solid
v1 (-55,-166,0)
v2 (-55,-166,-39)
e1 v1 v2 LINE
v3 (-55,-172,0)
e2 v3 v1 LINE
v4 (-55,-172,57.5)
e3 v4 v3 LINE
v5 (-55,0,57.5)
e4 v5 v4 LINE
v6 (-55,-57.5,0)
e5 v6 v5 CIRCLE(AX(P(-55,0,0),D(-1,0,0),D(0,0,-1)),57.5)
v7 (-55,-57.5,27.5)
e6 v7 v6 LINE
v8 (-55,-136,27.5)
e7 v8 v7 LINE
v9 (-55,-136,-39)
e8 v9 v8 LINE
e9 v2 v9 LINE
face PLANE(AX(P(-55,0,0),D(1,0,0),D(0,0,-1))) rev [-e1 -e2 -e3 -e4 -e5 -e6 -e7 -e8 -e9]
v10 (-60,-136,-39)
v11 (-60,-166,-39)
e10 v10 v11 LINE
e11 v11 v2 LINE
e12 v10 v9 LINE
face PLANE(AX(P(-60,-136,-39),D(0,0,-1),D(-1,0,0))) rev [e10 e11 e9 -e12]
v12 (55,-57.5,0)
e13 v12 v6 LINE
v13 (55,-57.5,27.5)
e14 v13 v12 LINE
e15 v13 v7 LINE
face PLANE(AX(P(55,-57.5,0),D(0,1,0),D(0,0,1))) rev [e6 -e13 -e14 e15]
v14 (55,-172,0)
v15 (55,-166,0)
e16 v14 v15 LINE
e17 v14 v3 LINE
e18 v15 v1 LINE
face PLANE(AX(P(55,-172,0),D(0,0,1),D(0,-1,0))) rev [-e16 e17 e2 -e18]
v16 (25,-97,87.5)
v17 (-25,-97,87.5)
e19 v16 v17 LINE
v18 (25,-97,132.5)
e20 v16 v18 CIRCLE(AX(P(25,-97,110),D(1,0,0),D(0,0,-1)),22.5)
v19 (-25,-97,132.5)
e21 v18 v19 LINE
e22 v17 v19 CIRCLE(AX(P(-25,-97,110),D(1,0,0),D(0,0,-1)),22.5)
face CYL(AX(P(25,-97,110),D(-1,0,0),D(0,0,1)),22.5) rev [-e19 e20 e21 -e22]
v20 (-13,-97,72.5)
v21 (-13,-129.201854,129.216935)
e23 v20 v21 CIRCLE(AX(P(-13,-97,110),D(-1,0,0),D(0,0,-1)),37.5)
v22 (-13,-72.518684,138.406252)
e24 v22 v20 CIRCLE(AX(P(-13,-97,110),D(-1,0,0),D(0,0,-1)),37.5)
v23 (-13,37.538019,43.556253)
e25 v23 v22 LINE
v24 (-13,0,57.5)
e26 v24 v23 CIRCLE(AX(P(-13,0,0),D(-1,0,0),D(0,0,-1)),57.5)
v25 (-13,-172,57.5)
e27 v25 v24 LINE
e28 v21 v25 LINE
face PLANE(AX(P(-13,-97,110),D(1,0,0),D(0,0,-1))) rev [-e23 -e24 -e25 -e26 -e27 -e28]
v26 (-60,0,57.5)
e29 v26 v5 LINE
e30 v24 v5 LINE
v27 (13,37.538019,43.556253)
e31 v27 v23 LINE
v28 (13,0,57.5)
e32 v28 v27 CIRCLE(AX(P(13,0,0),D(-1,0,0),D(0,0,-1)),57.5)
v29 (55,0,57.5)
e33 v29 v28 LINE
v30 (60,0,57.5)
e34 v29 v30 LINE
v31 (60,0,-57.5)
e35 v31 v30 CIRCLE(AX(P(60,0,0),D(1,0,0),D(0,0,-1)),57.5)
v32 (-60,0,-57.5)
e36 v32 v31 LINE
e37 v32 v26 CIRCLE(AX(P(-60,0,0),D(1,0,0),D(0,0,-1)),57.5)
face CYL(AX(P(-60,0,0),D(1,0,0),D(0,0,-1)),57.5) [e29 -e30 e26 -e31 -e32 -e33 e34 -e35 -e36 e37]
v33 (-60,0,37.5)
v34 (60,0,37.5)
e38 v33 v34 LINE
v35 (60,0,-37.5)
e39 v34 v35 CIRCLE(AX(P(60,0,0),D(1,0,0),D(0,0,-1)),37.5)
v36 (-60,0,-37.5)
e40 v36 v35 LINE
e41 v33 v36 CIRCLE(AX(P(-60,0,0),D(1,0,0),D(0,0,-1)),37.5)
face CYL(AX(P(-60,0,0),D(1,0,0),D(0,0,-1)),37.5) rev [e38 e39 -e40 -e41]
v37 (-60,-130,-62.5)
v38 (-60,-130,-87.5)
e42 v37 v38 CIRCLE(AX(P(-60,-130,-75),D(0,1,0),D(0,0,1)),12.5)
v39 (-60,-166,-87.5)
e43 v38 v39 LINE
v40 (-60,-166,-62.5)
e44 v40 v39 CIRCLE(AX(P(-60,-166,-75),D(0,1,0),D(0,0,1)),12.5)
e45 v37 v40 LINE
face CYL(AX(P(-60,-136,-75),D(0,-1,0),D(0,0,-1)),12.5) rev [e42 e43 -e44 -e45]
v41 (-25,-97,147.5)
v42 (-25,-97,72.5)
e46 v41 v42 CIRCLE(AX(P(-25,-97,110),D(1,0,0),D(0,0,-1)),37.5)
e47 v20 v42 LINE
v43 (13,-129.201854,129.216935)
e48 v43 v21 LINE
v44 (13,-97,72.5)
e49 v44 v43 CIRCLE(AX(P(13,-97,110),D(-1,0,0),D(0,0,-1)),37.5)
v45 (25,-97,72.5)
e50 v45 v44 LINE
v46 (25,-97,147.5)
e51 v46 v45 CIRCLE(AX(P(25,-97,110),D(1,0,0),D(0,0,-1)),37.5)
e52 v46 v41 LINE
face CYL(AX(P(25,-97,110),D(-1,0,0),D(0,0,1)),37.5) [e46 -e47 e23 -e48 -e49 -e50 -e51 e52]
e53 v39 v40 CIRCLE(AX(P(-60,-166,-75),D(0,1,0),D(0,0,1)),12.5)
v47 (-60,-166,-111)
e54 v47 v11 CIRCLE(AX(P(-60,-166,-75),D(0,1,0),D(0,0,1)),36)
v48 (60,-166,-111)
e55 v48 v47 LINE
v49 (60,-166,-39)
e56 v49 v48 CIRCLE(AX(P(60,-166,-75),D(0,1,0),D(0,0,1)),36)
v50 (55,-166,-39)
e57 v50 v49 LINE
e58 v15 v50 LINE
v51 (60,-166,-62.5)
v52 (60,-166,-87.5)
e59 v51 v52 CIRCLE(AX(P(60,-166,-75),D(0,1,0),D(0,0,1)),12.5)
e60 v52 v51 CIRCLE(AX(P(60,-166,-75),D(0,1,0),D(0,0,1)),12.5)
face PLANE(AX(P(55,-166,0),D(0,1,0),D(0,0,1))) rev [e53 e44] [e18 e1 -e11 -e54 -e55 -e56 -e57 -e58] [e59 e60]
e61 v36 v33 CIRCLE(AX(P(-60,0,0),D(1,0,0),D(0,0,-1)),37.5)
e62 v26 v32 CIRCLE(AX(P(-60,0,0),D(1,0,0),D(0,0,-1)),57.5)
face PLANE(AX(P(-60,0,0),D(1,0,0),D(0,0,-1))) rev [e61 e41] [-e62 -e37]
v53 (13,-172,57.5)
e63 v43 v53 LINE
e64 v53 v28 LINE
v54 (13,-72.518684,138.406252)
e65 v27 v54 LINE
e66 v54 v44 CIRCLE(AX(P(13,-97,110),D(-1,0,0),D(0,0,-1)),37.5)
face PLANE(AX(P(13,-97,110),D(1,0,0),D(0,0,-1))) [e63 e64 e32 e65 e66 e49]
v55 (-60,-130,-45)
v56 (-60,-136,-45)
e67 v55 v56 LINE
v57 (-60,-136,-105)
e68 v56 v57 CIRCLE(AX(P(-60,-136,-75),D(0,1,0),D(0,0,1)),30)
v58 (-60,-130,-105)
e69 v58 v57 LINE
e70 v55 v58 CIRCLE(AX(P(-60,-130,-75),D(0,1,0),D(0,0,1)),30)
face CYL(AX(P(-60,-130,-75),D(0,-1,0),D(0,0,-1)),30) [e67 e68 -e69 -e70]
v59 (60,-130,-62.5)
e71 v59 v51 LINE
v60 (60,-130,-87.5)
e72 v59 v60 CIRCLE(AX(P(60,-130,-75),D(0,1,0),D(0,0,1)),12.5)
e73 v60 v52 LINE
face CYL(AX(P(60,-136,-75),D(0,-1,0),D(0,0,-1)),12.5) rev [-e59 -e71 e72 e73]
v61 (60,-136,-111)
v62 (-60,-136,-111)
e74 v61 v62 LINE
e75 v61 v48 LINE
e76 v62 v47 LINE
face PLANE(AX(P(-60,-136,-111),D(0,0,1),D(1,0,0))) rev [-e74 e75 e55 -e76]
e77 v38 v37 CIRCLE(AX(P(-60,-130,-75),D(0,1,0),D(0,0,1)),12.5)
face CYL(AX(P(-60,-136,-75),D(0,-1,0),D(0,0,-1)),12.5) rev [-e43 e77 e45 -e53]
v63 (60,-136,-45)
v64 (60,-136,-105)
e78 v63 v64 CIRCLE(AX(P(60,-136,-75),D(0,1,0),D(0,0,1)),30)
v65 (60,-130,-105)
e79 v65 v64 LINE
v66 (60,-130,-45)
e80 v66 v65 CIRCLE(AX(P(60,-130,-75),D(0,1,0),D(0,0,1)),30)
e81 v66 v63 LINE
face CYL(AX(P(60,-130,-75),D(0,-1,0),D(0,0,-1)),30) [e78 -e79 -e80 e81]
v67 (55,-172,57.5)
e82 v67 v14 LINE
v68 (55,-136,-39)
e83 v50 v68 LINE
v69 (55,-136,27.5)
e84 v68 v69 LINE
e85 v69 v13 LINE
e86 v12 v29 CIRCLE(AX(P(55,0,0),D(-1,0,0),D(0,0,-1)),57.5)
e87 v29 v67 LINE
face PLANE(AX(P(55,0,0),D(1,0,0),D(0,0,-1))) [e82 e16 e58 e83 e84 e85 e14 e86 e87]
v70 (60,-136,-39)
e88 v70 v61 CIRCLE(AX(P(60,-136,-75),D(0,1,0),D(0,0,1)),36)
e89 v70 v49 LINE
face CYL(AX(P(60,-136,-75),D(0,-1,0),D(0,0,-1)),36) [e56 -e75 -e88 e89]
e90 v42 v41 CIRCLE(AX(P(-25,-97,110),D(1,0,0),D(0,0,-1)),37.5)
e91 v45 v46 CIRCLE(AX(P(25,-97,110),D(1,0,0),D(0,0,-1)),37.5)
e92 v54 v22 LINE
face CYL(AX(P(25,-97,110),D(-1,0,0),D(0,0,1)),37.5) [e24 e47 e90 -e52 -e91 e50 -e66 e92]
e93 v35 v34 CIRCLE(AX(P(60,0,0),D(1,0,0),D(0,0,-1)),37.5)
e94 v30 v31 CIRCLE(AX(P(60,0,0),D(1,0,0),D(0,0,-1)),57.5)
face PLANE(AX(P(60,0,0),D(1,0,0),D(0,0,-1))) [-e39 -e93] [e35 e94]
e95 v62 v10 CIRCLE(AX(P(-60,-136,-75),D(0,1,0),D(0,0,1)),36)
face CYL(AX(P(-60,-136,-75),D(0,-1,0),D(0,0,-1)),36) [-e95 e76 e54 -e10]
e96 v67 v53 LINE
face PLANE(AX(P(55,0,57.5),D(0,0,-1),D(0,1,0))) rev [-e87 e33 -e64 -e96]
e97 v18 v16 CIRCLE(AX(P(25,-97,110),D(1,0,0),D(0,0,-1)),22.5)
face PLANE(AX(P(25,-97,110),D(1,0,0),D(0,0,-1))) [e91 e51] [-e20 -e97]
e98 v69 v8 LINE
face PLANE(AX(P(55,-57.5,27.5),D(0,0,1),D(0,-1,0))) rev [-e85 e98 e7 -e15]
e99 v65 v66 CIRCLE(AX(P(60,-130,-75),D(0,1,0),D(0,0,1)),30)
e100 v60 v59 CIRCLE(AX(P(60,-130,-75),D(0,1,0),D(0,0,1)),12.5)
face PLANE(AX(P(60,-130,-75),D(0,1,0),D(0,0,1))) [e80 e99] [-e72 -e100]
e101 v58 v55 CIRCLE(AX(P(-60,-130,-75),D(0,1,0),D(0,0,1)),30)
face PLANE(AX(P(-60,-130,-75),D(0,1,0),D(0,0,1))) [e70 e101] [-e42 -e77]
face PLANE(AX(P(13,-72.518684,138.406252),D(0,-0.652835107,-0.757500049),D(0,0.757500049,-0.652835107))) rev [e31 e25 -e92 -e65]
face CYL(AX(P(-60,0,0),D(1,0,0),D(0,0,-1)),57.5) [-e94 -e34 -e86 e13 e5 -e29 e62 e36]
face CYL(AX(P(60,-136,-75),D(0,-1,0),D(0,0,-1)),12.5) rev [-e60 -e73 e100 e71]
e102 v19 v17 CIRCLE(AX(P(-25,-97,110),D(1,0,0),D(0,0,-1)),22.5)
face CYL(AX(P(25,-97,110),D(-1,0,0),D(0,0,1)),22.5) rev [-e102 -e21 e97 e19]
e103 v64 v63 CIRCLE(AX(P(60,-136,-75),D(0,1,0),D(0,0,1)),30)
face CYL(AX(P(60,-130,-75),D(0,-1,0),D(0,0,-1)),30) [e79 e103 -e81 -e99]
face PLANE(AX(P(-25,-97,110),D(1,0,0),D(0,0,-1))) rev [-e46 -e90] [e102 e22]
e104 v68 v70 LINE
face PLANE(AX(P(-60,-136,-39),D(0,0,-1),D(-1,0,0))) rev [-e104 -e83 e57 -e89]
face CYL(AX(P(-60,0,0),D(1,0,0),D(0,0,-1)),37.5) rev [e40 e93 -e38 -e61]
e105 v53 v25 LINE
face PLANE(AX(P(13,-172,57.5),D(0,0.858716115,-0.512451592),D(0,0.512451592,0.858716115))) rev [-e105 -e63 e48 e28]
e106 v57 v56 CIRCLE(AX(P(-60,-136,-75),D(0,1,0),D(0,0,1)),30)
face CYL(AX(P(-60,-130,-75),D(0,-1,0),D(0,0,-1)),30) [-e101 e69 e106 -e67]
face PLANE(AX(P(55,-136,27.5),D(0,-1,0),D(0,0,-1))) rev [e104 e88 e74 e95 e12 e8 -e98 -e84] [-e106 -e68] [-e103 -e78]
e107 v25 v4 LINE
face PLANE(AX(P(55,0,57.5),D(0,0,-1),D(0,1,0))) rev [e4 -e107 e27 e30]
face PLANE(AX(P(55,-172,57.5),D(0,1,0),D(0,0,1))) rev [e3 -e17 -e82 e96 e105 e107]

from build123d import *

# Parameters (mm, degrees)
BEARING_HOUSING_SKETCH_R   = 57.5
BEARING_HOUSING_SKETCH_R_2 = 37.5
BEARING_HOUSING_115_DEPTH  = 60
BASE_FOOT_SKETCH_R         = 12.5
BASE_FOOT_DEPTH            = 30
MOUNTING_PAD_SKETCH_R      = 30
MOUNTING_PAD_SKETCH_R_2    = 12.5
MOUNTING_PAD_DEPTH         = 6
SUPPORT_WEB_DEPTH          = 55
SIDE_BOSS_SKETCH_R         = 37.5
SIDE_BOSS_SKETCH_R_2       = 22.5
SIDE_BOSS_75_DEPTH         = 25
GUSSET_RIB_DEPTH           = 13


with BuildPart() as part:
    # Bearing Housing Sketch → Bearing Housing Ø115 (new, symmetric)
    with BuildSketch(Plane(origin=(0, 0, 0), x_dir=(0, 0, -1), z_dir=(1, 0, 0))):
        Circle(BEARING_HOUSING_SKETCH_R)
        Circle(BEARING_HOUSING_SKETCH_R_2, mode=Mode.SUBTRACT)
    extrude(amount=BEARING_HOUSING_115_DEPTH, both=True)



with BuildPart() as body_2:
    # Base Foot Sketch → Base Foot (new body)
    with BuildSketch(Plane(origin=(0, -166, 0), x_dir=(1, 0, 0), z_dir=(0, 1, 0))):
        with BuildLine():
            Line((-60, 111), (60, 111))
            ThreePointArc((60, 111), (96, 75), (60, 39))
            Line((60, 39), (-60, 39))
            ThreePointArc((-60, 39), (-96, 75), (-60, 111))
        make_face()
        with Locations(Location((60, 75, 0), (0, 0, 270))):
            Circle(BASE_FOOT_SKETCH_R, mode=Mode.SUBTRACT)
        with Locations(Location((-60, 75, 0), (0, 0, 270))):
            Circle(BASE_FOOT_SKETCH_R, mode=Mode.SUBTRACT)
    extrude(amount=BASE_FOOT_DEPTH)

    # Mounting Pad Sketch → Mounting Pad (add)
    # profile 1 of 2: a face of its own
    with BuildSketch(Plane(origin=(0, -136, 0), x_dir=(1, 0, 0), z_dir=(0, 1, 0))):
        with Locations(Location((60, 75, 0), (0, 0, 270))):
            Circle(MOUNTING_PAD_SKETCH_R)
        with Locations(Location((60, 75, 0), (0, 0, 270))):
            Circle(MOUNTING_PAD_SKETCH_R_2, mode=Mode.SUBTRACT)
    # profile 2 of 2: a face of its own
    with BuildSketch(Plane(origin=(0, -136, 0), x_dir=(1, 0, 0), z_dir=(0, 1, 0))):
        with Locations(Location((-60, 75, 0), (0, 0, 270))):
            Circle(MOUNTING_PAD_SKETCH_R)
        with Locations(Location((-60, 75, 0), (0, 0, 270))):
            Circle(MOUNTING_PAD_SKETCH_R_2, mode=Mode.SUBTRACT)
    extrude(amount=MOUNTING_PAD_DEPTH)


with BuildPart() as part_1:
    add(part.part)

    add(body_2.part)  # Support Web merges body 2
    # Support Web Sketch → Support Web (add, symmetric)
    with BuildSketch(Plane(origin=(0, 0, 0), x_dir=(0, 0, -1), z_dir=(1, 0, 0))):
        with BuildLine():
            Line((-57.5, 0), (-57.5, -172))
            Line((-57.5, -172), (0, -172))
            Line((0, -172), (0, -166))
            Line((0, -166), (39, -166))
            Line((39, -166), (39, -136))
            Line((39, -136), (-27.5, -136))
            Line((-27.5, -136), (-27.5, -57.5))
            Line((-27.5, -57.5), (0, -57.5))
            ThreePointArc((0, -57.5), (-40.658639918, -40.658639918), (-57.5, 0))
        make_face()
    extrude(amount=SUPPORT_WEB_DEPTH, both=True)



with BuildPart() as body_2_2:
    # Side Boss Sketch → Side Boss Ø75 (new, symmetric)
    with BuildSketch(Plane(origin=(0, 0, 0), x_dir=(0, 0, -1), z_dir=(1, 0, 0))):
        with Locations((-110, -97)):
            Circle(SIDE_BOSS_SKETCH_R)
        with Locations((-110, -97)):
            Circle(SIDE_BOSS_SKETCH_R_2, mode=Mode.SUBTRACT)
    extrude(amount=SIDE_BOSS_75_DEPTH, both=True)


with BuildPart() as part_2:
    add(part_1.part)

    add(body_2_2.part)  # Gusset Rib merges body 2 2
    # Gusset Rib Sketch → Gusset Rib (add, symmetric)
    with BuildSketch(Plane(origin=(0, 0, 0), x_dir=(0, 0, -1), z_dir=(1, 0, 0))):
        with BuildLine():
            Line((-138.406251821, -72.518683502), (-43.556252792, 37.53801863))
            ThreePointArc((-43.556252792, 37.53801863), (-53.901458865, 20.022056144), (-57.5, 0))
            Line((-57.5, 0), (-57.5, -172))
            Line((-57.5, -172), (-129.216934712, -129.201854299))
            ThreePointArc((-129.216934712, -129.201854299), (-72.983281658, -90.998953157), (-138.406251821, -72.518683502))
        make_face()
    extrude(amount=GUSSET_RIB_DEPTH, both=True)


solid = part_2.part
